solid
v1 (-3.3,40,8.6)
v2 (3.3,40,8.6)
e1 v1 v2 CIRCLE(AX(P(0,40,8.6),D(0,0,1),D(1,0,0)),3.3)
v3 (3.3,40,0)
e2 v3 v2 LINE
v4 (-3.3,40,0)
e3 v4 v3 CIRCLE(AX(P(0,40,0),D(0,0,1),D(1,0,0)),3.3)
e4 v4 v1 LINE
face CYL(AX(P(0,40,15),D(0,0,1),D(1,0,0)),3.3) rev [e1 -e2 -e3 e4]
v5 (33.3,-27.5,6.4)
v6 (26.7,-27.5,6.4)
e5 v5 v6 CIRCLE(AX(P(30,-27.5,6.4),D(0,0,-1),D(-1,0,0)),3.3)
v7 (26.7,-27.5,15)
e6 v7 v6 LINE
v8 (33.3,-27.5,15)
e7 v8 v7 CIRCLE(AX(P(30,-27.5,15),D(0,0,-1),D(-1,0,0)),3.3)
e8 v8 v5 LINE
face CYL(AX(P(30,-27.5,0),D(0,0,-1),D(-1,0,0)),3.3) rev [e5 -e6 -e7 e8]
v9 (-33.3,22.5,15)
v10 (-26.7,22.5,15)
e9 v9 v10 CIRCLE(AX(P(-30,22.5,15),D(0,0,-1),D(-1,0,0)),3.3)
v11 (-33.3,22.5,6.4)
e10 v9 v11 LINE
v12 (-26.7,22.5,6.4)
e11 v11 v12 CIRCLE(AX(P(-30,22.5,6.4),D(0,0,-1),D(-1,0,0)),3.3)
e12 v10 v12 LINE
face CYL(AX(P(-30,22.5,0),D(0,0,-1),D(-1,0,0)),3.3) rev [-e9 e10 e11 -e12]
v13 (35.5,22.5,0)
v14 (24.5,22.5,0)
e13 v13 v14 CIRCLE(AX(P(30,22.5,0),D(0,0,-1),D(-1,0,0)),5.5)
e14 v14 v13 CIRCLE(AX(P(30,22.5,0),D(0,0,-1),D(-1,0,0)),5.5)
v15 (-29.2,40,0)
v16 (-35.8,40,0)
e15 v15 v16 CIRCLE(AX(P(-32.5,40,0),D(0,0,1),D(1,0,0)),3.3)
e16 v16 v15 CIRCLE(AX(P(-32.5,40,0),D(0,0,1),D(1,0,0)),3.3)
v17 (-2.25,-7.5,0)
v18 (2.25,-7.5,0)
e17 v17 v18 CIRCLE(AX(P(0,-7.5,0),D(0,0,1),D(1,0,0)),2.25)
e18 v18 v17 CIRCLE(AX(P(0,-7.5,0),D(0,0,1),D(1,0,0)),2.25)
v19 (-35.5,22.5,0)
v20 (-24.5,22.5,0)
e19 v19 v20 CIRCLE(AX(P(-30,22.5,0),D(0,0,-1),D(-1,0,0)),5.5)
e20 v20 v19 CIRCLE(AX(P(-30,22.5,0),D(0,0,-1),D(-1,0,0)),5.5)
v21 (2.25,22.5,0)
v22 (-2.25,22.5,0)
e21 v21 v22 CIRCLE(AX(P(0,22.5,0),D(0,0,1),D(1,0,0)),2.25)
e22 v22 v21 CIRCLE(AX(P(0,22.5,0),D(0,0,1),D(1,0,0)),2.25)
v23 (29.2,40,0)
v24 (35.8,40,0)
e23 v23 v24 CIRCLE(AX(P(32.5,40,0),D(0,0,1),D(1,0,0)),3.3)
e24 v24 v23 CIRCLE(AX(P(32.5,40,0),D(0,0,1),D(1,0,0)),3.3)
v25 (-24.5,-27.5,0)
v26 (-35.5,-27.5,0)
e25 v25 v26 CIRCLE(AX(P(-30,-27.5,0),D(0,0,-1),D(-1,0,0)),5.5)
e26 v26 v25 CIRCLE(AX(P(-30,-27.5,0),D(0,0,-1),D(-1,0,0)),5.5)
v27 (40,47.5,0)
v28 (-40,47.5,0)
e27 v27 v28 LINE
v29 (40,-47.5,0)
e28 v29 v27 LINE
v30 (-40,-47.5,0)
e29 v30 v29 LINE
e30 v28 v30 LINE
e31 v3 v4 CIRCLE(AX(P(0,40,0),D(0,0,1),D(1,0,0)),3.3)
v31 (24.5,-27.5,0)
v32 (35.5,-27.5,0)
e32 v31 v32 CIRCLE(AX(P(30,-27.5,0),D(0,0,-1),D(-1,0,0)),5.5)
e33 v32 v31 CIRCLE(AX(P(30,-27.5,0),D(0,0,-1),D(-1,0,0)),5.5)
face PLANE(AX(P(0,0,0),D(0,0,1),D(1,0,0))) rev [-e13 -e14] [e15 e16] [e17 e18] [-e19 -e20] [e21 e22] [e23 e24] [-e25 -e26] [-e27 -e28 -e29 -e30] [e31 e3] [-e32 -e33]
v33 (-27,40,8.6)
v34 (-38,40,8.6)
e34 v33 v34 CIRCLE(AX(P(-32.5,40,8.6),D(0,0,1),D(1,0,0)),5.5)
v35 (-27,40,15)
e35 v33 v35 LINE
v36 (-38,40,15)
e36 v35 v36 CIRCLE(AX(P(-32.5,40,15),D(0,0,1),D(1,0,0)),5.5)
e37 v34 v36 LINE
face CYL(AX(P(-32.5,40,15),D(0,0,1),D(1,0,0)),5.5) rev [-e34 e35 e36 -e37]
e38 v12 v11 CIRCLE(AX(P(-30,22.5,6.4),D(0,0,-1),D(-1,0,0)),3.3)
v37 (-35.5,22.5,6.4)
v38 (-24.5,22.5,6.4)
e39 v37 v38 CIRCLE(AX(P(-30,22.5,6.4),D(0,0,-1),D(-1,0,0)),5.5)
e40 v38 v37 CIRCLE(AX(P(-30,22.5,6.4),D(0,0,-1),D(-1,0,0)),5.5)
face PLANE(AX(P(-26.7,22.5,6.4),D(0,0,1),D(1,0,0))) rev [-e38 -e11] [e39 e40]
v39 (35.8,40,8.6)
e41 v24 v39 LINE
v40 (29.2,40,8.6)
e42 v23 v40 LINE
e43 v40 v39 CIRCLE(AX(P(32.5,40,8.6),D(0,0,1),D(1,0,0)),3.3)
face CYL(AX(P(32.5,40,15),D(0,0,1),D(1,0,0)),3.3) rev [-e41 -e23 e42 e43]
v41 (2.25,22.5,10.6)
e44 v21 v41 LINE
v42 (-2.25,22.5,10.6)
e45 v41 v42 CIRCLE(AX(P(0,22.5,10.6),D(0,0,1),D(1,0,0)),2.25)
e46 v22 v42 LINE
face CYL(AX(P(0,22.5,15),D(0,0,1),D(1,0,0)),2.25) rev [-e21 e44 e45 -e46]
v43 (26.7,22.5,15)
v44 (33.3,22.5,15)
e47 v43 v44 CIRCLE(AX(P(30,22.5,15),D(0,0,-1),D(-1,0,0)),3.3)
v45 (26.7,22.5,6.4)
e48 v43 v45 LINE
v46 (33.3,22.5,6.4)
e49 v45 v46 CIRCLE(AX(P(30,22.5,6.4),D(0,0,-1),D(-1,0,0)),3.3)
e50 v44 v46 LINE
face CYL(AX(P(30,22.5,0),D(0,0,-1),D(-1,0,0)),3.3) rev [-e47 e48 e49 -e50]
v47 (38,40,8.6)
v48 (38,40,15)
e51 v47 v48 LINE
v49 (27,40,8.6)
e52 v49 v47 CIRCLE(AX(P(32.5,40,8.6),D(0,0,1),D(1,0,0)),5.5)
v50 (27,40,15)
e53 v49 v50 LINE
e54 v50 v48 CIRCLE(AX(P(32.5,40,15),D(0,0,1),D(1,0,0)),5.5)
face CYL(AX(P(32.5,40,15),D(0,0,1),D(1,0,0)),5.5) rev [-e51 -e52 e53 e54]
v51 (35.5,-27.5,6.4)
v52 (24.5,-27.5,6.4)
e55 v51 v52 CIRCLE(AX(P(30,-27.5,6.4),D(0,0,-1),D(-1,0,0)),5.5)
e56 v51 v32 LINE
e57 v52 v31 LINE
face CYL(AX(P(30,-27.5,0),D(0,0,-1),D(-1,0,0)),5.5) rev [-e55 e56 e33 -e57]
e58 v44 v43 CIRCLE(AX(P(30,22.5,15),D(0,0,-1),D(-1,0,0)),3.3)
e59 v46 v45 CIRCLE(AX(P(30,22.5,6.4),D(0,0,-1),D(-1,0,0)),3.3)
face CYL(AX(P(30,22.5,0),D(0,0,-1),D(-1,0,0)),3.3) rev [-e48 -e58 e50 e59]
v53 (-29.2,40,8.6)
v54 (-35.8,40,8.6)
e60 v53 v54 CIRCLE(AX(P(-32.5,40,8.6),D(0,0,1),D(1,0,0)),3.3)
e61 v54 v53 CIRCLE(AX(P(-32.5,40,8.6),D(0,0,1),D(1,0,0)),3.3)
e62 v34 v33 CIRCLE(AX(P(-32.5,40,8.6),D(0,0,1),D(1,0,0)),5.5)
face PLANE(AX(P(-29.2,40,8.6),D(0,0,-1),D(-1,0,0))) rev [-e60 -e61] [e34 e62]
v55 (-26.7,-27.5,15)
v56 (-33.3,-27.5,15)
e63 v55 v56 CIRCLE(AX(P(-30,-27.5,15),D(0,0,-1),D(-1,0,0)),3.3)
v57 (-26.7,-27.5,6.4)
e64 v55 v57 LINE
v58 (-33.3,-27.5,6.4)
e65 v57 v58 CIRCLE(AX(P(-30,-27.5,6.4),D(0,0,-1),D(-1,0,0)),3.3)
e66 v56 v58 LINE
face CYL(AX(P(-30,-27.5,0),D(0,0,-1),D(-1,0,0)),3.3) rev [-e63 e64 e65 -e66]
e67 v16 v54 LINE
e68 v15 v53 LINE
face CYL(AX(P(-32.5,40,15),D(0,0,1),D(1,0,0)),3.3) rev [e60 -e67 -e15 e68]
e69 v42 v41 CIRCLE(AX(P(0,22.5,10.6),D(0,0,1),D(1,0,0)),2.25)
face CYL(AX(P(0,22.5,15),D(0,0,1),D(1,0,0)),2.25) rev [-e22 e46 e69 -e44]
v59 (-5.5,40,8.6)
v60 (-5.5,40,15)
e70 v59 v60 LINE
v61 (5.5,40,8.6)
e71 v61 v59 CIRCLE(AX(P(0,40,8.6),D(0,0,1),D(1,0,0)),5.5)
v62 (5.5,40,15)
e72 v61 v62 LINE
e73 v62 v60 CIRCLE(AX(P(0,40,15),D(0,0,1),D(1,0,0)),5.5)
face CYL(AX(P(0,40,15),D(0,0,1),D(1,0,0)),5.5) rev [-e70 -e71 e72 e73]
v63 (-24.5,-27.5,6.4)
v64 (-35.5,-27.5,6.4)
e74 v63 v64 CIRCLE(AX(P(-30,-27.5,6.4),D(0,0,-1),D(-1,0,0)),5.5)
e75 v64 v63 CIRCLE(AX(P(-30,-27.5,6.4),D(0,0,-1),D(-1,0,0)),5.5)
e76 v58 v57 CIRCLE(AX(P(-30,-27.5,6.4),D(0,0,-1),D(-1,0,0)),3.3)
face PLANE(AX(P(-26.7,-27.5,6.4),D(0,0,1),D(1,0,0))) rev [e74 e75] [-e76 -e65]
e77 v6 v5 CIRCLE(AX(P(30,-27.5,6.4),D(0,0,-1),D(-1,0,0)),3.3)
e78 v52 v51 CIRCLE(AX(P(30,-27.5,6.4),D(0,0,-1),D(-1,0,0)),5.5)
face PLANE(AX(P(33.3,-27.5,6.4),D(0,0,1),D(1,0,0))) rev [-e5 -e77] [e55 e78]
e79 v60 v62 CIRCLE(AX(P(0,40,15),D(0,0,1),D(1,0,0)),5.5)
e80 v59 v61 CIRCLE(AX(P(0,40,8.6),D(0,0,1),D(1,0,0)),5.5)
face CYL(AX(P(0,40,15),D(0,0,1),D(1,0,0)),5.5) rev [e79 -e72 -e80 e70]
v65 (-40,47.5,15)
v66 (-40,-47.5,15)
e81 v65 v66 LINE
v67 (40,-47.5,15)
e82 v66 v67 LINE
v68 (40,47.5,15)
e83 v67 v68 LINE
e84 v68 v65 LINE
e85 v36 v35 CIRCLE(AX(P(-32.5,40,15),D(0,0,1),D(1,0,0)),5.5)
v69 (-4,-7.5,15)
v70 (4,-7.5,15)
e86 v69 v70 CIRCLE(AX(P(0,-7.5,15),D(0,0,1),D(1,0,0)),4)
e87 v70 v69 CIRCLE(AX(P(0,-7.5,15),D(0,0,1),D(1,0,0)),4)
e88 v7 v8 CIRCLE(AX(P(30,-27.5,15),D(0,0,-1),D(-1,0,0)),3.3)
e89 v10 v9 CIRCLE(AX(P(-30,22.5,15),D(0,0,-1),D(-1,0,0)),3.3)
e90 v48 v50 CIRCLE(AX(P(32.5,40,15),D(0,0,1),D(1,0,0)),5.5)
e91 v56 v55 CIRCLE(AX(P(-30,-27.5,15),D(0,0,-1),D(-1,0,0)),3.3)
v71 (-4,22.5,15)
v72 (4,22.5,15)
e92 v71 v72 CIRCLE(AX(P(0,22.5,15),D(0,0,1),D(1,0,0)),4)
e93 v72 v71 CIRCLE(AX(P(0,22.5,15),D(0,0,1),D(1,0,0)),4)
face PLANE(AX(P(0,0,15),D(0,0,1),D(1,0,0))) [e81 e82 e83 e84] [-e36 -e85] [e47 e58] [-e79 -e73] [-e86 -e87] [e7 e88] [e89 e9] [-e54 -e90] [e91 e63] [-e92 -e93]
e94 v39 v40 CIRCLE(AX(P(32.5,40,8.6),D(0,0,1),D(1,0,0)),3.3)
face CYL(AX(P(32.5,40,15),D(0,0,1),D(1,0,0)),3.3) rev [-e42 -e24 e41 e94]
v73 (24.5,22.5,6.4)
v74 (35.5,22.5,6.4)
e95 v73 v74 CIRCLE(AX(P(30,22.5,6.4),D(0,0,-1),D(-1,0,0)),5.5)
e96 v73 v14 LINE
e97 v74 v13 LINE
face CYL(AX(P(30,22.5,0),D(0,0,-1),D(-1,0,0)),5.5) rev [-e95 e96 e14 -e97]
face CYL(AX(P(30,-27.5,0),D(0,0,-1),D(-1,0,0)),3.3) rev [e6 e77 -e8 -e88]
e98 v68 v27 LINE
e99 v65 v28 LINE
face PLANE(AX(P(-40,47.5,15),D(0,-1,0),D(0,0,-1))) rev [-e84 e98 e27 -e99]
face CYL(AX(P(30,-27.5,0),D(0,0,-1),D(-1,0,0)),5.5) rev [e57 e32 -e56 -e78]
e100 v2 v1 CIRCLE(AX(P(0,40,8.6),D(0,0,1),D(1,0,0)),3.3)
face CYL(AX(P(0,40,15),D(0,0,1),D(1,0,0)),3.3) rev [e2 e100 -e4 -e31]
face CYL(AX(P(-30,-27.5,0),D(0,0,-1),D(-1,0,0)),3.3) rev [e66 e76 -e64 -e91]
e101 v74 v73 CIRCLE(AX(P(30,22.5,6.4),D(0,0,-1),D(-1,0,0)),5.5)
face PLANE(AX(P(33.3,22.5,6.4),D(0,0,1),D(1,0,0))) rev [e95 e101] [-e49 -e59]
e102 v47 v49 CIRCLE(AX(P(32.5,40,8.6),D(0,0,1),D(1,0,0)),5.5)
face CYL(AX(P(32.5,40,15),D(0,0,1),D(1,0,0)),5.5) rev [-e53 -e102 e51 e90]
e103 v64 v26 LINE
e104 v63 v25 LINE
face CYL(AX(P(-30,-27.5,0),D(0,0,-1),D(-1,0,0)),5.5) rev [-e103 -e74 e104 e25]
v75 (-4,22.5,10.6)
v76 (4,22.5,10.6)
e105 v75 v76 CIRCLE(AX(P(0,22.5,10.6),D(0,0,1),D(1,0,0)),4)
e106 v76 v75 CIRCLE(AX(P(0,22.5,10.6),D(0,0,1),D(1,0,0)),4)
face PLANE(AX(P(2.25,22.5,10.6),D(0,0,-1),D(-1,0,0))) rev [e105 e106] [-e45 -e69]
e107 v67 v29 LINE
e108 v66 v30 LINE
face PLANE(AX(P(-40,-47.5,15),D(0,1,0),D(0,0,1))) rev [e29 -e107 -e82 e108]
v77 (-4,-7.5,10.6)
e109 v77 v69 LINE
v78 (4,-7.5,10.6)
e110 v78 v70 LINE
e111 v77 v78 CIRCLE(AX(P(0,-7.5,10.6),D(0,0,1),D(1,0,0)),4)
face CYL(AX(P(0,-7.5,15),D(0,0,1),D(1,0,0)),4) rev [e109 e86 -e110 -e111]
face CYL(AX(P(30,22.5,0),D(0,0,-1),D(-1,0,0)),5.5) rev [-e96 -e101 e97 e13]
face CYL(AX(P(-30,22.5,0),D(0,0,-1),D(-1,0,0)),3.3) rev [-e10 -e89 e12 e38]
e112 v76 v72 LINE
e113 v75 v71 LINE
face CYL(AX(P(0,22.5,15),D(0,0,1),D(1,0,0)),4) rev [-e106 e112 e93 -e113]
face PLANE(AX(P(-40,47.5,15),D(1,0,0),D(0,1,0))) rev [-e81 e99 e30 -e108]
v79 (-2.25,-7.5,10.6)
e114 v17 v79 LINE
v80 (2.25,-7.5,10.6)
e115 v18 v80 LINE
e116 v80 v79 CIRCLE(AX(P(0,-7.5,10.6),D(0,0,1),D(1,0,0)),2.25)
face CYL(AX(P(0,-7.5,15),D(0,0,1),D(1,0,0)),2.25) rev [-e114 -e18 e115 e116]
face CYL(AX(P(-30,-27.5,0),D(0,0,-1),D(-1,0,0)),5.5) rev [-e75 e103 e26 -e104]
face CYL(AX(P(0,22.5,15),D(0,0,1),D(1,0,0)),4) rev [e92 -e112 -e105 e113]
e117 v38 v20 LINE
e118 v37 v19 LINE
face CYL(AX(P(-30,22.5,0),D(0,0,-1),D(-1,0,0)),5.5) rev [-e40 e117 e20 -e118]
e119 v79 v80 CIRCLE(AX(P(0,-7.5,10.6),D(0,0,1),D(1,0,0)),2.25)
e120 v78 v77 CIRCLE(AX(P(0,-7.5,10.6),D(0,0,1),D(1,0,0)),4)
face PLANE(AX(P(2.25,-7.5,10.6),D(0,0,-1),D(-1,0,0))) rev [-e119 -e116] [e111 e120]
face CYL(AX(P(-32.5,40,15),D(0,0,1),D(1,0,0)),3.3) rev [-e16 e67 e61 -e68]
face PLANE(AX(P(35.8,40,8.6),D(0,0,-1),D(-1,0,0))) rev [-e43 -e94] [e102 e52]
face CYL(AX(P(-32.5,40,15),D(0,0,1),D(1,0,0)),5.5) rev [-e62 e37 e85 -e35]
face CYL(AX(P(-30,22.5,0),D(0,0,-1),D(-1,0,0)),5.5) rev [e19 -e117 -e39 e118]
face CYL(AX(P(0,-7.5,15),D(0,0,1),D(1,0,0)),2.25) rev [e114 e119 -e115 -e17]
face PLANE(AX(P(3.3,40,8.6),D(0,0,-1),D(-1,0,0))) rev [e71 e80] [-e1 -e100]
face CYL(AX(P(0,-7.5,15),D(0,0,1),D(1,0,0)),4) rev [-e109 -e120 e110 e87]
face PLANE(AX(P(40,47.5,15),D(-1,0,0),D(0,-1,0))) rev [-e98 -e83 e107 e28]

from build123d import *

# Parameters (mm, degrees)
SKETCH_1_W                   = 80
SKETCH_1_H                   = 95
EXTRUDE_1_DEPTH              = 15
HOLE_WIZARD_M4_1_D           = 4.5
HOLE_WIZARD_M4_1_CBORE_D     = 8
HOLE_WIZARD_M4_1_CBORE_DEPTH = 4.4
HOLE_WIZARD_M6_1_D           = 6.6
HOLE_WIZARD_M6_1_CBORE_D     = 11
HOLE_WIZARD_M6_1_CBORE_DEPTH = 6.4
HOLE_WIZARD_M6_2_D           = 6.6
HOLE_WIZARD_M6_2_CBORE_D     = 11
HOLE_WIZARD_M6_2_CBORE_DEPTH = 6.4


with BuildPart() as part:
    # 草图1 → 凸台-拉伸1 (new body)
    with BuildSketch(Plane.XY):
        Rectangle(SKETCH_1_W, SKETCH_1_H)
    extrude(amount=EXTRUDE_1_DEPTH)

    # M4 六角凹头螺钉的柱形沉头孔1 (through all)
    with Locations(Plane.XY.offset(15)):
        with Locations((0, 22.5), (0, -7.5)):
            CounterBoreHole(HOLE_WIZARD_M4_1_D / 2, HOLE_WIZARD_M4_1_CBORE_D / 2, HOLE_WIZARD_M4_1_CBORE_DEPTH)

    # M6 六角凹头螺钉的柱形沉头孔1 (through all)
    with Locations(Plane(origin=(0, 0, 0), x_dir=(-1, 0, 0), z_dir=(0, 0, -1))):
        with Locations((-30, 22.5), (30, 22.5), (30, -27.5), (-30, -27.5)):
            CounterBoreHole(HOLE_WIZARD_M6_1_D / 2, HOLE_WIZARD_M6_1_CBORE_D / 2, HOLE_WIZARD_M6_1_CBORE_DEPTH)

    # M6 六角凹头螺钉的柱形沉头孔2 (through all)
    with Locations(Plane.XY.offset(15)):
        with Locations((-32.5, 40), (0, 40), (32.5, 40)):
            CounterBoreHole(HOLE_WIZARD_M6_2_D / 2, HOLE_WIZARD_M6_2_CBORE_D / 2, HOLE_WIZARD_M6_2_CBORE_DEPTH)


solid = part.part
